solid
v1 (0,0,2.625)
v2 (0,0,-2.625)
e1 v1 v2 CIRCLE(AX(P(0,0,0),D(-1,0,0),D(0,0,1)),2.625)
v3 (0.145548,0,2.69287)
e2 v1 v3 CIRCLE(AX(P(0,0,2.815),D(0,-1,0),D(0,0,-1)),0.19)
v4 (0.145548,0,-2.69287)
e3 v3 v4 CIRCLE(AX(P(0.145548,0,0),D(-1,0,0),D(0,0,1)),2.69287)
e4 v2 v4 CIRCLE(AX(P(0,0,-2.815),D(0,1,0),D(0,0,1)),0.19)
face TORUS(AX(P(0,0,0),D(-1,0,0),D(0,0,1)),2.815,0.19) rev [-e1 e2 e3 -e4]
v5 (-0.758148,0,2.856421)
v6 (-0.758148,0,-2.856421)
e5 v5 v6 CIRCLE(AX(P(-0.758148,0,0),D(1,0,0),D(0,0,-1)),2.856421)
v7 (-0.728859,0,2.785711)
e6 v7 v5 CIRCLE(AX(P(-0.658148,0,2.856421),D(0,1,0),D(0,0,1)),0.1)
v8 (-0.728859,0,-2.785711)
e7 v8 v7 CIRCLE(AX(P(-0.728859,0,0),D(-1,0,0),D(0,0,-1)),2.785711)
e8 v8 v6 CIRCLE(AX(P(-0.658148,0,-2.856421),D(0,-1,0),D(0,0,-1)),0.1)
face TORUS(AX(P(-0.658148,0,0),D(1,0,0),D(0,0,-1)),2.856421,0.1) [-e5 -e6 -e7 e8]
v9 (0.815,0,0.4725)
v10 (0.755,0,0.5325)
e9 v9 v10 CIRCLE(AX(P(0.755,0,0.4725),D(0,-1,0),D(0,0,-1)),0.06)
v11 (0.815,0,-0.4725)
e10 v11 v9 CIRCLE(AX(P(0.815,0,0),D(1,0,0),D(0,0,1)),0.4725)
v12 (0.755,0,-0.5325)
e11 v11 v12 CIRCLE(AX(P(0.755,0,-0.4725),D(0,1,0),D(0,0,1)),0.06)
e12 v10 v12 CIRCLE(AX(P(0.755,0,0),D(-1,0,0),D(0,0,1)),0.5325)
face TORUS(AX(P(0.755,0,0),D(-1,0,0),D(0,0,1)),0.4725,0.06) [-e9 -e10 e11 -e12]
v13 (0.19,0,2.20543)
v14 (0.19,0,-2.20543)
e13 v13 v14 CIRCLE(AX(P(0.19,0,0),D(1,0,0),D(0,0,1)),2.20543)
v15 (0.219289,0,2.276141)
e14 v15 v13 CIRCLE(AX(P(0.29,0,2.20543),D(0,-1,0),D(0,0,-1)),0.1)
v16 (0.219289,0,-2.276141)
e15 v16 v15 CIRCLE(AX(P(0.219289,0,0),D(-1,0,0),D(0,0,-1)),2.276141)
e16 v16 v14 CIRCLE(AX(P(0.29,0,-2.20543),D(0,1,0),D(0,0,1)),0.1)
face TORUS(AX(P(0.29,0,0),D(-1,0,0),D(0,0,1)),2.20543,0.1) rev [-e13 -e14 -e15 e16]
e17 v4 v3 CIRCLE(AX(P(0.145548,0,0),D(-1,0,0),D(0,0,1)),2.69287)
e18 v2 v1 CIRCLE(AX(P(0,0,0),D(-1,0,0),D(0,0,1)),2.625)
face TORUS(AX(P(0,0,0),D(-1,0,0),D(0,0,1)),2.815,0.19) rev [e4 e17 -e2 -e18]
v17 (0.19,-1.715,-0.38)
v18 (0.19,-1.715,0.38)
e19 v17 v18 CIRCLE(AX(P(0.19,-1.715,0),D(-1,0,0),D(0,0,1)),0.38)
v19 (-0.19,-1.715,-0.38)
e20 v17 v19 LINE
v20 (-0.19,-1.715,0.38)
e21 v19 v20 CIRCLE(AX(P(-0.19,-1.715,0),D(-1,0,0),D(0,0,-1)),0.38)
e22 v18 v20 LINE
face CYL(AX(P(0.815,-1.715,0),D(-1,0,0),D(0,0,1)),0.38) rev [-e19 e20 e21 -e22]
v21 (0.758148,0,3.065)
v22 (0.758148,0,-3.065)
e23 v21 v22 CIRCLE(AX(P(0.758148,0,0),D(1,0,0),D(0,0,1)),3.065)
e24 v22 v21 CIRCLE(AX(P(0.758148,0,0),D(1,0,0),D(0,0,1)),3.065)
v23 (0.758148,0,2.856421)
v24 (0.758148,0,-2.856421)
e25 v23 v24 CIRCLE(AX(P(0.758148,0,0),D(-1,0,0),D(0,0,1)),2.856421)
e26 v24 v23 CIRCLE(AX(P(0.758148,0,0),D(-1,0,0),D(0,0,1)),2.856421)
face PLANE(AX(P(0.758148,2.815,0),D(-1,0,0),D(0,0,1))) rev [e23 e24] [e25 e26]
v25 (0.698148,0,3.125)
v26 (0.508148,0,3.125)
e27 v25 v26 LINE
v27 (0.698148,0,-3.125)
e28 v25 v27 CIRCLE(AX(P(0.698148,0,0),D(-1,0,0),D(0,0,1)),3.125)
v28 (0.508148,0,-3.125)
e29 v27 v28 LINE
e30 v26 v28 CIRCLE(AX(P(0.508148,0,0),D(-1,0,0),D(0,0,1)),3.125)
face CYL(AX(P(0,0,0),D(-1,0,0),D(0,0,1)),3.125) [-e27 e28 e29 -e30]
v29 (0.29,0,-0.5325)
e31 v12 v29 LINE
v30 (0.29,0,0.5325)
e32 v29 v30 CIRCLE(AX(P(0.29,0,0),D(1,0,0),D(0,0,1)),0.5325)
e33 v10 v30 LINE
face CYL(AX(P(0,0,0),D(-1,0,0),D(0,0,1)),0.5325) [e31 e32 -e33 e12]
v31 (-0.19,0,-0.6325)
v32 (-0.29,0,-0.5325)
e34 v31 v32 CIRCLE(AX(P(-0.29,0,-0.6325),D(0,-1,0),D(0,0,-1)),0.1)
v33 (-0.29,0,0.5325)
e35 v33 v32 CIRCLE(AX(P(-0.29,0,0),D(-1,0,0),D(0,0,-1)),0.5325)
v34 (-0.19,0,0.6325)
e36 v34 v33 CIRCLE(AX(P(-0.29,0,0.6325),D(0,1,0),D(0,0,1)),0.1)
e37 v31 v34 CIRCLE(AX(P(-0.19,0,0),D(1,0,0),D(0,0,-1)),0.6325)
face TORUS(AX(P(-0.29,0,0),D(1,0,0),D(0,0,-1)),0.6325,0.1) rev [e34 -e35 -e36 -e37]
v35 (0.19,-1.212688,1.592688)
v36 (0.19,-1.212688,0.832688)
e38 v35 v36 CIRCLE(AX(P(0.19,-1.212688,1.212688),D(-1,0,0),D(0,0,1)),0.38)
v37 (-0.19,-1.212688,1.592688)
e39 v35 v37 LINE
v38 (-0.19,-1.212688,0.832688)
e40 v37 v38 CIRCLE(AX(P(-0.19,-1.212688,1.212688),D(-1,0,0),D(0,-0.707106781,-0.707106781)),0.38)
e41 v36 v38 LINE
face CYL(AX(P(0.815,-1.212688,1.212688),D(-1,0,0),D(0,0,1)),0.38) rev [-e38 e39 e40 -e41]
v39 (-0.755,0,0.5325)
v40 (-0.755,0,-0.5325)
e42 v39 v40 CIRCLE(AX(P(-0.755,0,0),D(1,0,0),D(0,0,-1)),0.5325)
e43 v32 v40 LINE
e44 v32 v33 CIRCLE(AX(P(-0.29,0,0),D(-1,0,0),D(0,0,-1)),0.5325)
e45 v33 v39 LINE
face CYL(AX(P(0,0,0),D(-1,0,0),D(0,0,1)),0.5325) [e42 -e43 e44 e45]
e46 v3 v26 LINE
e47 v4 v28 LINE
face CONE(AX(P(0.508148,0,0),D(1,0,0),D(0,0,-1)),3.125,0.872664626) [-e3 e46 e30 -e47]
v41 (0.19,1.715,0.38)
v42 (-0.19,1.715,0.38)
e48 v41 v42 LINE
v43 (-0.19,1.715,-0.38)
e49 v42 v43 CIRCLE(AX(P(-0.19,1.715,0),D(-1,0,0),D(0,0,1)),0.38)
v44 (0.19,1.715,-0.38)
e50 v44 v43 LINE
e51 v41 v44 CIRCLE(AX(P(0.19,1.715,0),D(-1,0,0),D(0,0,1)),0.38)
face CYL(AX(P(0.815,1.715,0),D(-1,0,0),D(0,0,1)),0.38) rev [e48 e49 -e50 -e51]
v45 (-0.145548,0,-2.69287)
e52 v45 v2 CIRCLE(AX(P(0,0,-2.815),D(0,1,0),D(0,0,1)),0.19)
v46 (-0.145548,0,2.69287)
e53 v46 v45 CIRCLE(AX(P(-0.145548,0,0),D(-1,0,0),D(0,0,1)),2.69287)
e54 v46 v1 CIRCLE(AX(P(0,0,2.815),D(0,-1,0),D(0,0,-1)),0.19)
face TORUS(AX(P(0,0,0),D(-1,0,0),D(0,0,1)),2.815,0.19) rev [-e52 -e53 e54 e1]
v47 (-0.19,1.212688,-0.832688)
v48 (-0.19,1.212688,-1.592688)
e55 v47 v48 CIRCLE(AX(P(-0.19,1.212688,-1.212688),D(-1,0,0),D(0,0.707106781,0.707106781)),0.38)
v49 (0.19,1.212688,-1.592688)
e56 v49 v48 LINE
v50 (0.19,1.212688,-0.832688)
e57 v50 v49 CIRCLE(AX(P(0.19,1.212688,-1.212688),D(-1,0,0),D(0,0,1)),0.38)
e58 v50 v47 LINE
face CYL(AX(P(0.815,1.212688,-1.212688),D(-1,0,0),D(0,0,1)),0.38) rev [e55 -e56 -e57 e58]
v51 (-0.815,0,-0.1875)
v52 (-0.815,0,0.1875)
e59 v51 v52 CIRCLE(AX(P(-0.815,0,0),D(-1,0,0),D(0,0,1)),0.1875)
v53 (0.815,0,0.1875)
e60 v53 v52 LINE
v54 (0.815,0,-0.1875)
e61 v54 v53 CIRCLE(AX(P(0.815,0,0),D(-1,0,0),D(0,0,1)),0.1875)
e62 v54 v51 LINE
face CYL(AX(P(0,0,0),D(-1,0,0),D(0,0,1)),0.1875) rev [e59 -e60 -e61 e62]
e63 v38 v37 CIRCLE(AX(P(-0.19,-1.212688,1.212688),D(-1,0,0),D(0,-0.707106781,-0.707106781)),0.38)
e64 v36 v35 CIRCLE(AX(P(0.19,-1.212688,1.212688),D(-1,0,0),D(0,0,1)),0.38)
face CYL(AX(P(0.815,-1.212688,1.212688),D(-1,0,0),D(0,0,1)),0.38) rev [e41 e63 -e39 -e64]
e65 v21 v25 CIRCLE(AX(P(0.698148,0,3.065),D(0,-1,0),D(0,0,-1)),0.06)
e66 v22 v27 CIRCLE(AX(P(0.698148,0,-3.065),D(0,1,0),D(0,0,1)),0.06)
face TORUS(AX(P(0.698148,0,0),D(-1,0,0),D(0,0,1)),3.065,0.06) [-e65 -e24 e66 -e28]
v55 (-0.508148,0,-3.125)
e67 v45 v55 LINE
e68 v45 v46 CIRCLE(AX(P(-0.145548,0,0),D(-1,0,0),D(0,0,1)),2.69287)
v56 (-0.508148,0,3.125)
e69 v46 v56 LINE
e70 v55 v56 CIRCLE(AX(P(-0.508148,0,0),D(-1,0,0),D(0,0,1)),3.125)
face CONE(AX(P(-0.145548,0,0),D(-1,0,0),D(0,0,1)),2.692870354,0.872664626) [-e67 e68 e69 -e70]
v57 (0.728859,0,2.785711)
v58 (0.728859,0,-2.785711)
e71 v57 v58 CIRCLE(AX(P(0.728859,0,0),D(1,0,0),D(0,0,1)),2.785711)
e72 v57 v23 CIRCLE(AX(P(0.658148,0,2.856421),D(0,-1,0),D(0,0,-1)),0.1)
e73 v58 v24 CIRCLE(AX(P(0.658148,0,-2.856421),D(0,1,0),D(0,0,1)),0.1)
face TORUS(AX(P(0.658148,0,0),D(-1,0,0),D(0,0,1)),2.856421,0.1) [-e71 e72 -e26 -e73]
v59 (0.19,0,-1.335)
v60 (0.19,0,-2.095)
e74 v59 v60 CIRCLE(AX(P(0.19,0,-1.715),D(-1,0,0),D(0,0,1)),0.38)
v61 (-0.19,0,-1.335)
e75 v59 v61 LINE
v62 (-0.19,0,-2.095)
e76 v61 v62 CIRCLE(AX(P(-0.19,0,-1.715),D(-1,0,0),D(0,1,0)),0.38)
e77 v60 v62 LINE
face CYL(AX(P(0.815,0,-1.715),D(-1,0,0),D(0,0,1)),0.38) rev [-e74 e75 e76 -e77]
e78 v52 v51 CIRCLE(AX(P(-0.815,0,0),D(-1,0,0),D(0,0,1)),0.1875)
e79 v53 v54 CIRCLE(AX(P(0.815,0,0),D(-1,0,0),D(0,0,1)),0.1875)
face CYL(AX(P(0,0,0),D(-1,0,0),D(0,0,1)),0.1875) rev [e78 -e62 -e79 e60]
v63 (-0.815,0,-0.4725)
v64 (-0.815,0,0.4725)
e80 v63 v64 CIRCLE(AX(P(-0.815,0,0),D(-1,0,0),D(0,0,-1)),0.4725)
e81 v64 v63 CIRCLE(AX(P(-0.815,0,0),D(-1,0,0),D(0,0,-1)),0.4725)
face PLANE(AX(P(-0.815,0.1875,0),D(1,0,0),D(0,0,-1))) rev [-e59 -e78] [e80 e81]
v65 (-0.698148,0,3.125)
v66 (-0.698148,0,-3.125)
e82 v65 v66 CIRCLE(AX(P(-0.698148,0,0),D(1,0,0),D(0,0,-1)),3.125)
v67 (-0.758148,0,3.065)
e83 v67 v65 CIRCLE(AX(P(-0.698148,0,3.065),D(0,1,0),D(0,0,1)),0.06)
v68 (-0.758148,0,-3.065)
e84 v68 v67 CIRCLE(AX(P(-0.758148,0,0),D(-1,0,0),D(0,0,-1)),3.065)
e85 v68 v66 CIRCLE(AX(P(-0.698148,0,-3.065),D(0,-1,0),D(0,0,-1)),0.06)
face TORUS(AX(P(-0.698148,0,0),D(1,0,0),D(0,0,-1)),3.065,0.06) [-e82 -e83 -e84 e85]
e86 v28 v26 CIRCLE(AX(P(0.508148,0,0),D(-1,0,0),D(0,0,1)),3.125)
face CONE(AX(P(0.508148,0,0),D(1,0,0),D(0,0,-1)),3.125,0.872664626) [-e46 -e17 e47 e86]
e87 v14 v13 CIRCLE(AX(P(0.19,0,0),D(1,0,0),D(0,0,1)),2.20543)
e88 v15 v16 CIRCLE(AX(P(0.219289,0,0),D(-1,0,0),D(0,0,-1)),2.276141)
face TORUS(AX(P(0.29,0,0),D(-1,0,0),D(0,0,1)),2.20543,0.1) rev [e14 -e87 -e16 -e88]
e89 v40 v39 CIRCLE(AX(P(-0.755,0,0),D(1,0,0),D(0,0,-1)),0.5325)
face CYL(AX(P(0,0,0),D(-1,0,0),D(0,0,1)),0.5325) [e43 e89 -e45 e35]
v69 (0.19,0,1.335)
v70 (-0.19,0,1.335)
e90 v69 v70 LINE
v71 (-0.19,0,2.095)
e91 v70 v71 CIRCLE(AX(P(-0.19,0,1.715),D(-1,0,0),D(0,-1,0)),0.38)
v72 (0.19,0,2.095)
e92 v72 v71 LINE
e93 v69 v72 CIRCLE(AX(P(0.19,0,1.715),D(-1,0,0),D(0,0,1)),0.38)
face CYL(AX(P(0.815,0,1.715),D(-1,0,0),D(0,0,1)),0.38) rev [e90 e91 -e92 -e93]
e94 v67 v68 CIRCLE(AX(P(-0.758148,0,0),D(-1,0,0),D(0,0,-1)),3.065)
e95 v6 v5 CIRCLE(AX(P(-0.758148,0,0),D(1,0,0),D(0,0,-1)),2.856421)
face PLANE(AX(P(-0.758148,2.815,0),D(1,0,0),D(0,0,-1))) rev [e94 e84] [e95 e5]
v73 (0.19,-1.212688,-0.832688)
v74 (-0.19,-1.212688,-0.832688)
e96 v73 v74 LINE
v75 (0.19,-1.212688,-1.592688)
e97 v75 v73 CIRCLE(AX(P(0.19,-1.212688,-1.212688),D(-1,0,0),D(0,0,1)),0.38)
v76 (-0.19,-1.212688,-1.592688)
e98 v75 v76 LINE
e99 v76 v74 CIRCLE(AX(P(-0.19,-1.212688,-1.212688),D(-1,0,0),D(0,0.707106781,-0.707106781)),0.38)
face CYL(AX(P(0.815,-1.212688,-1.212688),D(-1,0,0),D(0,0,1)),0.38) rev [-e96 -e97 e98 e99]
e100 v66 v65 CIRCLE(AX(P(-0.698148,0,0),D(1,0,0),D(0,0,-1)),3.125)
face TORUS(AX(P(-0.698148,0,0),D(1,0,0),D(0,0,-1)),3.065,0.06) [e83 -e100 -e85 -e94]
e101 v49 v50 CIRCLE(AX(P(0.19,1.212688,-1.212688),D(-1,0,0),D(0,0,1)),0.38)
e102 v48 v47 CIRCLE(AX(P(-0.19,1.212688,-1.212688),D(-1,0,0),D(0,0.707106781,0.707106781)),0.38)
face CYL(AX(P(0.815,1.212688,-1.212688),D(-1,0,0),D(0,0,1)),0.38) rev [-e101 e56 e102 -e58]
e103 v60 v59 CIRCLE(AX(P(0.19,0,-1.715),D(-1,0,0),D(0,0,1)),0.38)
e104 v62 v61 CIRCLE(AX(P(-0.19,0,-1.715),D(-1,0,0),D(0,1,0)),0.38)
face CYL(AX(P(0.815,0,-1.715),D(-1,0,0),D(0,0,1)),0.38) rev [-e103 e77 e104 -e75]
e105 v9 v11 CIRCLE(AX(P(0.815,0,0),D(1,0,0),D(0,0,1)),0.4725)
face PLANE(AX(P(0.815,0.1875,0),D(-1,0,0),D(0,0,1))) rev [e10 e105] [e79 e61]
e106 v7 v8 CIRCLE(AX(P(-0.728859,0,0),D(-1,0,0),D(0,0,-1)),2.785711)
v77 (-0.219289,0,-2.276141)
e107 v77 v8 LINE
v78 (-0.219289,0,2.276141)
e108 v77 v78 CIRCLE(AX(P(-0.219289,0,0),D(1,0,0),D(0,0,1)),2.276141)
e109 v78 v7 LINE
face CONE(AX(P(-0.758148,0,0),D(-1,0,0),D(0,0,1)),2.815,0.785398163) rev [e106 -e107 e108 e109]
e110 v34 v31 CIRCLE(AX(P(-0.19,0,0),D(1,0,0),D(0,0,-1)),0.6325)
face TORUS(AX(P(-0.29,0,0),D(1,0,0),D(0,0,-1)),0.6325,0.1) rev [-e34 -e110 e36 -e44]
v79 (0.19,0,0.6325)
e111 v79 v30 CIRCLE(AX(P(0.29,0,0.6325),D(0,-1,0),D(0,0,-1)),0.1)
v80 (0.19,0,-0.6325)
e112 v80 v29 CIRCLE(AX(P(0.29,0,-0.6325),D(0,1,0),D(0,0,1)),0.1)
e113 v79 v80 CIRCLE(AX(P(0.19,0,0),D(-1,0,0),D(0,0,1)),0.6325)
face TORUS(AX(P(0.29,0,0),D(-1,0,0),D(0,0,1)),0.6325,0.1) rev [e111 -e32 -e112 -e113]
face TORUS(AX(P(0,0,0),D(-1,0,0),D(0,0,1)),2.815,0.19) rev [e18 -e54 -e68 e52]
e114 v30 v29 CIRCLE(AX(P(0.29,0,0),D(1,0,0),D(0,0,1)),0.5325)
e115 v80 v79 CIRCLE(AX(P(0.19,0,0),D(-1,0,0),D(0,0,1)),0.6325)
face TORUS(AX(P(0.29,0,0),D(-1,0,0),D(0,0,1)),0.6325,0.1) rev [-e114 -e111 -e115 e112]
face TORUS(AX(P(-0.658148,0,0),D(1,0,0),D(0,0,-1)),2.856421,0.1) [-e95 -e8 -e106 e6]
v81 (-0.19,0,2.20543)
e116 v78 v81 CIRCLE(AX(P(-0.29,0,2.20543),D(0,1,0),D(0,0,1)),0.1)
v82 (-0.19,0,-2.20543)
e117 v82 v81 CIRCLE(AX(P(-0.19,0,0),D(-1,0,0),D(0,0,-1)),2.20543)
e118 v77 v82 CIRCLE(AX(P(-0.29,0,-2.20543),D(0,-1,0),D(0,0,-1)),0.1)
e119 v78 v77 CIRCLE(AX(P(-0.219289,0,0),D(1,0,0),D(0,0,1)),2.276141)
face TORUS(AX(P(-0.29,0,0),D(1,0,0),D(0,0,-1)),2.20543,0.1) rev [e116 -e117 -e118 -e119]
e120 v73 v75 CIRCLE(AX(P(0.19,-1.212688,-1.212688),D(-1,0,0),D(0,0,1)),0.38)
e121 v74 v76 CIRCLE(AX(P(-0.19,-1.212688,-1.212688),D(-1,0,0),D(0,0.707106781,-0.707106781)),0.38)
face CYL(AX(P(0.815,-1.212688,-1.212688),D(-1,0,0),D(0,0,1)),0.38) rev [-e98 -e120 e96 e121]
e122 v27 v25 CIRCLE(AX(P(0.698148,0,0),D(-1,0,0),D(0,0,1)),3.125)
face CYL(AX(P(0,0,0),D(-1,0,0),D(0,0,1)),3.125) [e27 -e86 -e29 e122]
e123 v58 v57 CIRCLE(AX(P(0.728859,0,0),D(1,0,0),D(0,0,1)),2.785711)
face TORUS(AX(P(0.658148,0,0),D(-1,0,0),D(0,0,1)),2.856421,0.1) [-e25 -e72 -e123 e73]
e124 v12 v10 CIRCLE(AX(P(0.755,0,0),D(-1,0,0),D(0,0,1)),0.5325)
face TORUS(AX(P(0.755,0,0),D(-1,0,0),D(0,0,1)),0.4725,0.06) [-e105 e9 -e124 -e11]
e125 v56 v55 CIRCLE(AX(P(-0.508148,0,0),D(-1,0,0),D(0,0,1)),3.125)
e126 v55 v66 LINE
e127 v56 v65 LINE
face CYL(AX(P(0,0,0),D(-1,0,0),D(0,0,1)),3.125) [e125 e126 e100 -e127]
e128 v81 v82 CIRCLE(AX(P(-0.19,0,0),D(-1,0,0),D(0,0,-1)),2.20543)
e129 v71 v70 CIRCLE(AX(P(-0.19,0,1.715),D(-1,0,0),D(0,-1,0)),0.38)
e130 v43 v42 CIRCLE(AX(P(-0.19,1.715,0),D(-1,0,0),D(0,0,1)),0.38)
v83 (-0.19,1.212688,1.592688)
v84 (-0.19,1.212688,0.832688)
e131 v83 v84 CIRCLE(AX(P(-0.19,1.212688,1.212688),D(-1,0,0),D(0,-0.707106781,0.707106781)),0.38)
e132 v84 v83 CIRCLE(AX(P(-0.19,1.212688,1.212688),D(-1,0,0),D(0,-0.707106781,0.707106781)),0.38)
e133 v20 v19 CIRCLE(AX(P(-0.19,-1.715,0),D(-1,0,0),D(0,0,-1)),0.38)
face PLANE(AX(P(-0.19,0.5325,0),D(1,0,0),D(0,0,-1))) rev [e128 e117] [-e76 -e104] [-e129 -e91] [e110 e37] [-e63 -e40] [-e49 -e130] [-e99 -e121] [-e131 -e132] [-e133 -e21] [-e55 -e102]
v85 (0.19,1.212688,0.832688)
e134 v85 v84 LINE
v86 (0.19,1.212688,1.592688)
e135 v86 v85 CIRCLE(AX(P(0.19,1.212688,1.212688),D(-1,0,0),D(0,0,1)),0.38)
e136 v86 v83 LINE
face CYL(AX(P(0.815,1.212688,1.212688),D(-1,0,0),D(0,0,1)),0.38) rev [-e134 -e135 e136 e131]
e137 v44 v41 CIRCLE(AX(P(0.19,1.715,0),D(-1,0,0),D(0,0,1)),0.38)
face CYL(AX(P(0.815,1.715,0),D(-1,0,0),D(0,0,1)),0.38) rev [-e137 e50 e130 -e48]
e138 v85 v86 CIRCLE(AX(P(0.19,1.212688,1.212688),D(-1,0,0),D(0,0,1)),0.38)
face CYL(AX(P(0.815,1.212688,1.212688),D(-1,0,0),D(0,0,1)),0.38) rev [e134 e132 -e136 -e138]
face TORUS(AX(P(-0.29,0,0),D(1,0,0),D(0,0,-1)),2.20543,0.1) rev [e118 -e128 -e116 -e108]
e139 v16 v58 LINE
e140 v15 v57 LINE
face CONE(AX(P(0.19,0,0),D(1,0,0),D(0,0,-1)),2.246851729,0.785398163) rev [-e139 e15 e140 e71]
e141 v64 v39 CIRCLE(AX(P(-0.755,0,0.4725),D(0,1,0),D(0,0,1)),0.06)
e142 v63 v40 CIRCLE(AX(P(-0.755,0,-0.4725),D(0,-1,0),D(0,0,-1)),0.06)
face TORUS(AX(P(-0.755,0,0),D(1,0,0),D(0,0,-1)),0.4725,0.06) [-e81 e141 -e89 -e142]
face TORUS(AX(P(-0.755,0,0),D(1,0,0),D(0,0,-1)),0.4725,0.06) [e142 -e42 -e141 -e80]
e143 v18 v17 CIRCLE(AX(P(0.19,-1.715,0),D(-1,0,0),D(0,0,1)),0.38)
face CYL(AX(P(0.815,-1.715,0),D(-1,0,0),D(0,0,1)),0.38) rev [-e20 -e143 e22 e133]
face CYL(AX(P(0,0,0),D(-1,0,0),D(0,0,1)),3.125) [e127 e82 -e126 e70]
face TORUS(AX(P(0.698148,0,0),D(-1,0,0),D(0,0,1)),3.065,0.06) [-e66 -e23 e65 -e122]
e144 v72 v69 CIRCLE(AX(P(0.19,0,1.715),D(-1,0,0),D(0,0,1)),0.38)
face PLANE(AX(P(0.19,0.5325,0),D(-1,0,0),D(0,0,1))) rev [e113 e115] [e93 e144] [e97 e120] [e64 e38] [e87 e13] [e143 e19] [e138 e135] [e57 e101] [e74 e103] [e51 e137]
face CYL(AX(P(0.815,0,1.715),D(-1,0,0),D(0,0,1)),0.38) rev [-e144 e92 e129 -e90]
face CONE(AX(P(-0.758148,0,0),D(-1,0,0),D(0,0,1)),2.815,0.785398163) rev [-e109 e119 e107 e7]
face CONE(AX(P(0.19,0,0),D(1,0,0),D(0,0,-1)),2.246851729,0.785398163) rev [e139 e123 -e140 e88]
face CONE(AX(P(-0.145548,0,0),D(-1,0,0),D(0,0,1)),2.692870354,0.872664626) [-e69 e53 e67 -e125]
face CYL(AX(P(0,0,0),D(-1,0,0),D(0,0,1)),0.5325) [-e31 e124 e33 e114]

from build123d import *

# Parameters (mm, degrees)
EDGE_FILLETS_R0_06_SET_1_R      = 0.06
WEB_FILLET_R0_1_R               = 0.1
EDGE_FILLETS_R0_06_SET_2_R      = 0.06
BOLT_HOLE_SKETCH_R              = 0.38
BOLT_HOLE_0_76_DEPTH            = 5.532248476
BOLT_CIRCLE_HOLES_8X_0_76_COUNT = 8


with BuildPart() as part:
    # Pulley Profile Sketch → Pulley Body Revolve (revolve)
    with BuildSketch(Plane.XY, mode=Mode.PRIVATE) as pulley_body_revolve_sk:
        with BuildLine():
            Line((-0.815, 0.1875), (0.815, 0.1875))
            Line((0.815, 0.1875), (0.815, 0.5325))
            Line((0.815, 0.5325), (0.19, 0.5325))
            Line((0.19, 0.5325), (0.19, 2.246851729))
            Line((0.19, 2.246851729), (0.758148271, 2.815))
            Line((0.758148271, 2.815), (0.758148271, 3.125))
            Line((0.758148271, 3.125), (0.508148271, 3.125))
            Line((0.508148271, 3.125), (0.145548444, 2.692870354))
            ThreePointArc((0.145548444, 2.692870354), (0, 2.625), (-0.145548444, 2.692870354))
            Line((-0.145548444, 2.692870354), (-0.508148271, 3.125))
            Line((-0.508148271, 3.125), (-0.758148271, 3.125))
            Line((-0.758148271, 3.125), (-0.758148271, 2.815))
            Line((-0.758148271, 2.815), (-0.19, 2.246851729))
            Line((-0.19, 2.246851729), (-0.19, 0.5325))
            Line((-0.19, 0.5325), (-0.815, 0.5325))
            Line((-0.815, 0.5325), (-0.815, 0.1875))
        make_face()
    revolve(pulley_body_revolve_sk.sketch.rotate(Axis((0, 0, 0), (1, 0, 0)), 90), axis=Axis((0, 0, 0), (1, 0, 0)))

    # Edge Fillets R0.06 Set 1
    edge_fillets_r0_06_set_1_edges = [part.edges().sort_by_distance(p)[0] for p in [
        (-0.758148271, 0, -3.125),
        (0.758148271, 0, -3.125),
    ]]
    fillet(edge_fillets_r0_06_set_1_edges, radius=EDGE_FILLETS_R0_06_SET_1_R)

    # Web Fillet R0.1
    web_fillet_r0_1_edges = [part.edges().sort_by_distance(p)[0] for p in [
        (-0.19, 0, -0.5325),
        (-0.19, 0, -2.246851729),
        (-0.758148271, 0, -2.815),
        (0.758148271, 0, -2.815),
        (0.19, 0, -2.246851729),
        (0.19, 0, -0.5325),
    ]]
    fillet(web_fillet_r0_1_edges, radius=WEB_FILLET_R0_1_R)

    # Edge Fillets R0.06 Set 2
    edge_fillets_r0_06_set_2_edges = [part.edges().sort_by_distance(p)[0] for p in [
        (0.815, 0, -0.5325),
        (-0.815, 0, -0.5325),
    ]]
    fillet(edge_fillets_r0_06_set_2_edges, radius=EDGE_FILLETS_R0_06_SET_2_R)

    # Bolt Hole Sketch → Bolt Hole Ø0.76 (cut, through all)
    with BuildSketch(Plane.ZY.offset(0.19)):
        with Locations((0, 1.715)):
            Circle(BOLT_HOLE_SKETCH_R)
    bolt_hole_0_76 = extrude(amount=-BOLT_HOLE_0_76_DEPTH, mode=Mode.SUBTRACT)

    # Bolt Circle Holes 8xØ0.76: Bolt Hole Ø0.76 ×8 about axis
    bolt_circle_holes_8x_0_76_axis = Axis((0, 0, 0), (1, 0, 0))
    for i in range(1, BOLT_CIRCLE_HOLES_8X_0_76_COUNT):
        add(bolt_hole_0_76.rotate(bolt_circle_holes_8x_0_76_axis, i * 360 / BOLT_CIRCLE_HOLES_8X_0_76_COUNT), mode=Mode.SUBTRACT)


solid = part.part
